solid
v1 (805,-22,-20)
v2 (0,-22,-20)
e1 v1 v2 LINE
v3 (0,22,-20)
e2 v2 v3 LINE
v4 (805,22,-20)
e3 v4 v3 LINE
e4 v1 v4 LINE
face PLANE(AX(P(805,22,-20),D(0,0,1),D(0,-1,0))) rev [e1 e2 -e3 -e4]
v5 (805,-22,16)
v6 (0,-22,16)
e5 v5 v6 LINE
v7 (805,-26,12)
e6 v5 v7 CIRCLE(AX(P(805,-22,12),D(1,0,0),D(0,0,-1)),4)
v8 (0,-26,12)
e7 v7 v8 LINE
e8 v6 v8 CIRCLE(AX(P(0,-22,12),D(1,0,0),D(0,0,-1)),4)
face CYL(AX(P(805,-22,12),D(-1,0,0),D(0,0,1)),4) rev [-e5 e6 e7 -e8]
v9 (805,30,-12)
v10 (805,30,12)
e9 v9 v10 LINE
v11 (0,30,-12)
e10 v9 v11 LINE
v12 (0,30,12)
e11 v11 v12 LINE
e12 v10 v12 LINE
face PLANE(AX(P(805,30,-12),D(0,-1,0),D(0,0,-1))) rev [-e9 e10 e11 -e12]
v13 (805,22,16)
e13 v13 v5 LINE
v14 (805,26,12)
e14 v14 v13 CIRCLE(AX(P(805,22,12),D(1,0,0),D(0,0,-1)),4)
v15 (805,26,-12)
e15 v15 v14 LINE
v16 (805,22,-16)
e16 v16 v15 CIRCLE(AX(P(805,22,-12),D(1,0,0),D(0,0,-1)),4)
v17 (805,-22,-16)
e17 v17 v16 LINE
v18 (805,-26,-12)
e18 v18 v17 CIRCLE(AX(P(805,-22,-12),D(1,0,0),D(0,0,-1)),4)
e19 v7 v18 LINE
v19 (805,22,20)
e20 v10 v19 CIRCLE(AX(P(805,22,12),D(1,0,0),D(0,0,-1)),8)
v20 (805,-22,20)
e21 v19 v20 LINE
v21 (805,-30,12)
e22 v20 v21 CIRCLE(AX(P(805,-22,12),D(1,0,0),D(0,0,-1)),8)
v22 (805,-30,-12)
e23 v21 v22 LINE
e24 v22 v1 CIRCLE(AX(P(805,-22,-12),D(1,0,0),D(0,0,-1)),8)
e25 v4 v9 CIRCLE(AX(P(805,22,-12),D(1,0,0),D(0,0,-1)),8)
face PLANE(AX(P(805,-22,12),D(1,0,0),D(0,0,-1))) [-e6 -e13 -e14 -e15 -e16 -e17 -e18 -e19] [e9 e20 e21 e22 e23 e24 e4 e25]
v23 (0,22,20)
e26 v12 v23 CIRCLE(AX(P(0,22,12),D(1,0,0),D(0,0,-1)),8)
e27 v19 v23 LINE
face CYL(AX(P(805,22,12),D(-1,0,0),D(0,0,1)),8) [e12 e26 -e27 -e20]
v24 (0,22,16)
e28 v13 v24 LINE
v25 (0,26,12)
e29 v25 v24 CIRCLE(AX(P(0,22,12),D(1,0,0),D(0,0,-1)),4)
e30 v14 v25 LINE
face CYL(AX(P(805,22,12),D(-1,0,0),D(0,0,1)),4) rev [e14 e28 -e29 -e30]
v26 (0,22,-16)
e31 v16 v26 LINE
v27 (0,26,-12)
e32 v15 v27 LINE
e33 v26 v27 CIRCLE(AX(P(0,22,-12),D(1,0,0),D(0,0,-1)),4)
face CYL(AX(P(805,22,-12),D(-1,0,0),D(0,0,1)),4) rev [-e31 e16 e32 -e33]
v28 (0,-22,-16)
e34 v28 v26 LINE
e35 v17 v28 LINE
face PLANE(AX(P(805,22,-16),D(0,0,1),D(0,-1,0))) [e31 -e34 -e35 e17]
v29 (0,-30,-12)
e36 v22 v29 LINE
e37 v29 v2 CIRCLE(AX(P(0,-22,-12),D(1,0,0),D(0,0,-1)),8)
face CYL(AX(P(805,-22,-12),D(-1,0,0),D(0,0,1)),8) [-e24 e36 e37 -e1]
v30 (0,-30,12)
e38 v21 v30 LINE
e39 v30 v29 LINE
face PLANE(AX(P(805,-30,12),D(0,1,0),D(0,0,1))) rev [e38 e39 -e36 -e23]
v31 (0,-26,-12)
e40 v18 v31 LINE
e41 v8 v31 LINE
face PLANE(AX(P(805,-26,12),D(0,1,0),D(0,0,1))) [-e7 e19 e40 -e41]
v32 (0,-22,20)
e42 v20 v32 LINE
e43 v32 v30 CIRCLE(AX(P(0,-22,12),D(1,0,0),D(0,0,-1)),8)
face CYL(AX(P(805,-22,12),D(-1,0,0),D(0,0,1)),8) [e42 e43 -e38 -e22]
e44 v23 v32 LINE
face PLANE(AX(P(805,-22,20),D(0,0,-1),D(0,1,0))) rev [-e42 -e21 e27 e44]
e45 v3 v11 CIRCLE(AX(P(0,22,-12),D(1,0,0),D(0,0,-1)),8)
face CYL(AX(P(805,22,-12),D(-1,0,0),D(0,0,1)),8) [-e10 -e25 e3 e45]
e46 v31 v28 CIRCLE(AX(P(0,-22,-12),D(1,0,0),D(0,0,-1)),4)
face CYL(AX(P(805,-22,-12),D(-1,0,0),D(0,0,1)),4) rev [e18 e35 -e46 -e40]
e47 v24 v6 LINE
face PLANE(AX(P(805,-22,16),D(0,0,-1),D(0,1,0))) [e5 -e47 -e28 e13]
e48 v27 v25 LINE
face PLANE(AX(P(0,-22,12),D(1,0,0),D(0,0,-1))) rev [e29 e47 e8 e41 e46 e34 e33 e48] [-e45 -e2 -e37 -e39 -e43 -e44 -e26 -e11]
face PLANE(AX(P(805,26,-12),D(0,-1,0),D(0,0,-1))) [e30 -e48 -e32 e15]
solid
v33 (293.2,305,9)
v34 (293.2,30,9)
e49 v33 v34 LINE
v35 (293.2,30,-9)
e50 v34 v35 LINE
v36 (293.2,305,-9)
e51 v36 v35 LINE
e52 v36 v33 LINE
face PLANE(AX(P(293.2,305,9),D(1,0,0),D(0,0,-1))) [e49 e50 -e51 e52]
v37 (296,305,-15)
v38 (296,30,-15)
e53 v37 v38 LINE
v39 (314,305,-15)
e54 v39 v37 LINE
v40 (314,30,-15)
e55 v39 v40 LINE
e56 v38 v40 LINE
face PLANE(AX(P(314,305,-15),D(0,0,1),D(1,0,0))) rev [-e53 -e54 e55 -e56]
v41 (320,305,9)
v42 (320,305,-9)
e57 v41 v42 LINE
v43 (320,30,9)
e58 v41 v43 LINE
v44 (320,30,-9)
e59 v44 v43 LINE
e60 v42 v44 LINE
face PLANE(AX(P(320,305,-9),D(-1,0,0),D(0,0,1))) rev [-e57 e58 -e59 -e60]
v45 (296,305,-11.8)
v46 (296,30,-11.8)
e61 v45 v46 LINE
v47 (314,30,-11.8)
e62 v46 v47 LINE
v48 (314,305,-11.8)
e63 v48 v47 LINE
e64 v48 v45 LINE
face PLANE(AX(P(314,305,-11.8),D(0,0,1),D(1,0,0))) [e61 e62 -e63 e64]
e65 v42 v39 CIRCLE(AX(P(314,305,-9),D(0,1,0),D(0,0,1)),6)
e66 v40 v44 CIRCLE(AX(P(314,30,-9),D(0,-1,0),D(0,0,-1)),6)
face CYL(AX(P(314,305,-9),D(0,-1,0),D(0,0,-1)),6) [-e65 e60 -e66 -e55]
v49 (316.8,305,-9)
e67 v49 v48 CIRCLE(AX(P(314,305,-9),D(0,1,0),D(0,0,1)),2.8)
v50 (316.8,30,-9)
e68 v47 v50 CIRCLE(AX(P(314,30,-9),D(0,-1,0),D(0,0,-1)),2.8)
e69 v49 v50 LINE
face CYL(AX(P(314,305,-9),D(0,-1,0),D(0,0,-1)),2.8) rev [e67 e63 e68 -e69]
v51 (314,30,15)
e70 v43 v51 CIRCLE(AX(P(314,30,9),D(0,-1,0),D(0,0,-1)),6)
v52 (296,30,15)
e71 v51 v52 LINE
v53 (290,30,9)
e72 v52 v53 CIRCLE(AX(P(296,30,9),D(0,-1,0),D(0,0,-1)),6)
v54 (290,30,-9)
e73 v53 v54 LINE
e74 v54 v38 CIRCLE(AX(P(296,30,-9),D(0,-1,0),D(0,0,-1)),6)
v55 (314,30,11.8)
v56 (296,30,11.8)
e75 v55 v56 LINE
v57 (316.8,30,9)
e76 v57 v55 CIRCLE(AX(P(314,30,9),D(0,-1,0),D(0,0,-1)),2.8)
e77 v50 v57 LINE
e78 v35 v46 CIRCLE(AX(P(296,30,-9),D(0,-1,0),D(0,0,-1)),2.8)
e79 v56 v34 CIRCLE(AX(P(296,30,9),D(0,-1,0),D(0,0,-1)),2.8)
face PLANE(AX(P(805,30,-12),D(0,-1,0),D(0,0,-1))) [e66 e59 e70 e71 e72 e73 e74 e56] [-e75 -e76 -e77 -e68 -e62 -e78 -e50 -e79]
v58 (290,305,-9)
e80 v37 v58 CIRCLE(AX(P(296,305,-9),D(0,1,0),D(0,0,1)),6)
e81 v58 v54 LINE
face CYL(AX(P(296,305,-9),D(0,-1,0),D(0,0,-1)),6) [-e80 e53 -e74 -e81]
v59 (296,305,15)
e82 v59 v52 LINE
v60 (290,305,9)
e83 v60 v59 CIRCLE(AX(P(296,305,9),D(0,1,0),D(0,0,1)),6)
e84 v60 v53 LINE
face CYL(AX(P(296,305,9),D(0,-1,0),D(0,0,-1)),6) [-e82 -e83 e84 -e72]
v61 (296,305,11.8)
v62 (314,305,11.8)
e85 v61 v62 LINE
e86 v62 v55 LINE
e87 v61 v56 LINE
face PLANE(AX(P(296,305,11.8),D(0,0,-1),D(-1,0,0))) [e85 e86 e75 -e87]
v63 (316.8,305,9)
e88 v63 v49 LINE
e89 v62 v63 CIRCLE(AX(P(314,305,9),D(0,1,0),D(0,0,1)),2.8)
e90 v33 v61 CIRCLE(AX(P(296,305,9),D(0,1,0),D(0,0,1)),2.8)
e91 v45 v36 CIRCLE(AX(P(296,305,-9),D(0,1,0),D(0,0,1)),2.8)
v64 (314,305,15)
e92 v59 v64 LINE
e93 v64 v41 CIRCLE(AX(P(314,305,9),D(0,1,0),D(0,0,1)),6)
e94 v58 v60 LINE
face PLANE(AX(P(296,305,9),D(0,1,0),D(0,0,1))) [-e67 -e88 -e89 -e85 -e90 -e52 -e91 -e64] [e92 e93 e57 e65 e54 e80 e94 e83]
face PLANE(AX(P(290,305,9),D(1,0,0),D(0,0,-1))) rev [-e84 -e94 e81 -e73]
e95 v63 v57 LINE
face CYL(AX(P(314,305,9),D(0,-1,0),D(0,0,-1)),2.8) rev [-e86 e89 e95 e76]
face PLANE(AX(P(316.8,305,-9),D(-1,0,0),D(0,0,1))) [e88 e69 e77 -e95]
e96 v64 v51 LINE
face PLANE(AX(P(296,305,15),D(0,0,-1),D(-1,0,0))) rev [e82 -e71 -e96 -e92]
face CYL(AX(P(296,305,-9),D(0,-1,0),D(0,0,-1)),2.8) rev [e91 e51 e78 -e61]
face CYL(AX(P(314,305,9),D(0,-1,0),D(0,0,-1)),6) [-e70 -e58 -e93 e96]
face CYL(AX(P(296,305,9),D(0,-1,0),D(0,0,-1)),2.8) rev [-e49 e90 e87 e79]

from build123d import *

# Parameters (mm, degrees)
GB_T_6728_2002_RECTANGULAR_HOLLOW_SECTIO_DEPTH = 805
GB_T_6728_2002_SQUARE_HOLLOW_SECTION_30_DEPTH  = 305


with BuildPart() as part:
    # Sketch12 → GB/T 6728-2002 rectangular hollow section 60X40X4(1) (new body)
    with BuildSketch(Plane(origin=(0, 0, 0), x_dir=(0, 0, 1), z_dir=(1, 0, 0))):
        with BuildLine():
            Line((-12, -30), (12, -30))
            ThreePointArc((12, -30), (17.656854249, -27.656854249), (20, -22))
            Line((20, -22), (20, 22))
            ThreePointArc((20, 22), (17.656854249, 27.656854249), (12, 30))
            Line((12, 30), (-12, 30))
            ThreePointArc((-12, 30), (-17.656854249, 27.656854249), (-20, 22))
            Line((-20, 22), (-20, -22))
            ThreePointArc((-20, -22), (-17.656854249, -27.656854249), (-12, -30))
        make_face()
        with BuildLine():
            Line((-12, -26), (12, -26))
            ThreePointArc((12, -26), (14.828427125, -24.828427125), (16, -22))
            Line((16, -22), (16, 22))
            ThreePointArc((16, 22), (14.828427125, 24.828427125), (12, 26))
            Line((12, 26), (-12, 26))
            ThreePointArc((-12, 26), (-14.828427125, 24.828427125), (-16, 22))
            Line((-16, 22), (-16, -22))
            ThreePointArc((-16, -22), (-14.828427125, -24.828427125), (-12, -26))
        make_face(mode=Mode.SUBTRACT)
    extrude(amount=GB_T_6728_2002_RECTANGULAR_HOLLOW_SECTIO_DEPTH)


with BuildPart() as body_2:
    # Sketch16 → GB/T 6728-2002 square hollow section 30×3.2(1) (new body)
    with BuildSketch(Plane(origin=(305, 0, 0), x_dir=(-1, 0, 0), z_dir=(0, 1, 0))):
        with BuildLine():
            Line((-9, -15), (9, -15))
            ThreePointArc((9, -15), (13.242640687, -13.242640687), (15, -9))
            Line((15, -9), (15, 9))
            ThreePointArc((15, 9), (13.242640687, 13.242640687), (9, 15))
            Line((9, 15), (-9, 15))
            ThreePointArc((-9, 15), (-13.242640687, 13.242640687), (-15, 9))
            Line((-15, 9), (-15, -9))
            ThreePointArc((-15, -9), (-13.242640687, -13.242640687), (-9, -15))
        make_face()
        with BuildLine():
            Line((-9, -11.8), (9, -11.8))
            ThreePointArc((9, -11.8), (10.979898987, -10.979898987), (11.8, -9))
            Line((11.8, -9), (11.8, 9))
            ThreePointArc((11.8, 9), (10.979898987, 10.979898987), (9, 11.8))
            Line((9, 11.8), (-9, 11.8))
            ThreePointArc((-9, 11.8), (-10.979898987, 10.979898987), (-11.8, 9))
            Line((-11.8, 9), (-11.8, -9))
            ThreePointArc((-11.8, -9), (-10.979898987, -10.979898987), (-9, -11.8))
        make_face(mode=Mode.SUBTRACT)
    extrude(amount=GB_T_6728_2002_SQUARE_HOLLOW_SECTION_30_DEPTH)

    # Trim_Extend1 9
    split(bisect_by=Plane(origin=(402.5, 30, 0), x_dir=(-1, 0, 0), z_dir=(0, 1, 0)), keep=Keep.TOP)


solid = Compound([part.part, body_2.part])
